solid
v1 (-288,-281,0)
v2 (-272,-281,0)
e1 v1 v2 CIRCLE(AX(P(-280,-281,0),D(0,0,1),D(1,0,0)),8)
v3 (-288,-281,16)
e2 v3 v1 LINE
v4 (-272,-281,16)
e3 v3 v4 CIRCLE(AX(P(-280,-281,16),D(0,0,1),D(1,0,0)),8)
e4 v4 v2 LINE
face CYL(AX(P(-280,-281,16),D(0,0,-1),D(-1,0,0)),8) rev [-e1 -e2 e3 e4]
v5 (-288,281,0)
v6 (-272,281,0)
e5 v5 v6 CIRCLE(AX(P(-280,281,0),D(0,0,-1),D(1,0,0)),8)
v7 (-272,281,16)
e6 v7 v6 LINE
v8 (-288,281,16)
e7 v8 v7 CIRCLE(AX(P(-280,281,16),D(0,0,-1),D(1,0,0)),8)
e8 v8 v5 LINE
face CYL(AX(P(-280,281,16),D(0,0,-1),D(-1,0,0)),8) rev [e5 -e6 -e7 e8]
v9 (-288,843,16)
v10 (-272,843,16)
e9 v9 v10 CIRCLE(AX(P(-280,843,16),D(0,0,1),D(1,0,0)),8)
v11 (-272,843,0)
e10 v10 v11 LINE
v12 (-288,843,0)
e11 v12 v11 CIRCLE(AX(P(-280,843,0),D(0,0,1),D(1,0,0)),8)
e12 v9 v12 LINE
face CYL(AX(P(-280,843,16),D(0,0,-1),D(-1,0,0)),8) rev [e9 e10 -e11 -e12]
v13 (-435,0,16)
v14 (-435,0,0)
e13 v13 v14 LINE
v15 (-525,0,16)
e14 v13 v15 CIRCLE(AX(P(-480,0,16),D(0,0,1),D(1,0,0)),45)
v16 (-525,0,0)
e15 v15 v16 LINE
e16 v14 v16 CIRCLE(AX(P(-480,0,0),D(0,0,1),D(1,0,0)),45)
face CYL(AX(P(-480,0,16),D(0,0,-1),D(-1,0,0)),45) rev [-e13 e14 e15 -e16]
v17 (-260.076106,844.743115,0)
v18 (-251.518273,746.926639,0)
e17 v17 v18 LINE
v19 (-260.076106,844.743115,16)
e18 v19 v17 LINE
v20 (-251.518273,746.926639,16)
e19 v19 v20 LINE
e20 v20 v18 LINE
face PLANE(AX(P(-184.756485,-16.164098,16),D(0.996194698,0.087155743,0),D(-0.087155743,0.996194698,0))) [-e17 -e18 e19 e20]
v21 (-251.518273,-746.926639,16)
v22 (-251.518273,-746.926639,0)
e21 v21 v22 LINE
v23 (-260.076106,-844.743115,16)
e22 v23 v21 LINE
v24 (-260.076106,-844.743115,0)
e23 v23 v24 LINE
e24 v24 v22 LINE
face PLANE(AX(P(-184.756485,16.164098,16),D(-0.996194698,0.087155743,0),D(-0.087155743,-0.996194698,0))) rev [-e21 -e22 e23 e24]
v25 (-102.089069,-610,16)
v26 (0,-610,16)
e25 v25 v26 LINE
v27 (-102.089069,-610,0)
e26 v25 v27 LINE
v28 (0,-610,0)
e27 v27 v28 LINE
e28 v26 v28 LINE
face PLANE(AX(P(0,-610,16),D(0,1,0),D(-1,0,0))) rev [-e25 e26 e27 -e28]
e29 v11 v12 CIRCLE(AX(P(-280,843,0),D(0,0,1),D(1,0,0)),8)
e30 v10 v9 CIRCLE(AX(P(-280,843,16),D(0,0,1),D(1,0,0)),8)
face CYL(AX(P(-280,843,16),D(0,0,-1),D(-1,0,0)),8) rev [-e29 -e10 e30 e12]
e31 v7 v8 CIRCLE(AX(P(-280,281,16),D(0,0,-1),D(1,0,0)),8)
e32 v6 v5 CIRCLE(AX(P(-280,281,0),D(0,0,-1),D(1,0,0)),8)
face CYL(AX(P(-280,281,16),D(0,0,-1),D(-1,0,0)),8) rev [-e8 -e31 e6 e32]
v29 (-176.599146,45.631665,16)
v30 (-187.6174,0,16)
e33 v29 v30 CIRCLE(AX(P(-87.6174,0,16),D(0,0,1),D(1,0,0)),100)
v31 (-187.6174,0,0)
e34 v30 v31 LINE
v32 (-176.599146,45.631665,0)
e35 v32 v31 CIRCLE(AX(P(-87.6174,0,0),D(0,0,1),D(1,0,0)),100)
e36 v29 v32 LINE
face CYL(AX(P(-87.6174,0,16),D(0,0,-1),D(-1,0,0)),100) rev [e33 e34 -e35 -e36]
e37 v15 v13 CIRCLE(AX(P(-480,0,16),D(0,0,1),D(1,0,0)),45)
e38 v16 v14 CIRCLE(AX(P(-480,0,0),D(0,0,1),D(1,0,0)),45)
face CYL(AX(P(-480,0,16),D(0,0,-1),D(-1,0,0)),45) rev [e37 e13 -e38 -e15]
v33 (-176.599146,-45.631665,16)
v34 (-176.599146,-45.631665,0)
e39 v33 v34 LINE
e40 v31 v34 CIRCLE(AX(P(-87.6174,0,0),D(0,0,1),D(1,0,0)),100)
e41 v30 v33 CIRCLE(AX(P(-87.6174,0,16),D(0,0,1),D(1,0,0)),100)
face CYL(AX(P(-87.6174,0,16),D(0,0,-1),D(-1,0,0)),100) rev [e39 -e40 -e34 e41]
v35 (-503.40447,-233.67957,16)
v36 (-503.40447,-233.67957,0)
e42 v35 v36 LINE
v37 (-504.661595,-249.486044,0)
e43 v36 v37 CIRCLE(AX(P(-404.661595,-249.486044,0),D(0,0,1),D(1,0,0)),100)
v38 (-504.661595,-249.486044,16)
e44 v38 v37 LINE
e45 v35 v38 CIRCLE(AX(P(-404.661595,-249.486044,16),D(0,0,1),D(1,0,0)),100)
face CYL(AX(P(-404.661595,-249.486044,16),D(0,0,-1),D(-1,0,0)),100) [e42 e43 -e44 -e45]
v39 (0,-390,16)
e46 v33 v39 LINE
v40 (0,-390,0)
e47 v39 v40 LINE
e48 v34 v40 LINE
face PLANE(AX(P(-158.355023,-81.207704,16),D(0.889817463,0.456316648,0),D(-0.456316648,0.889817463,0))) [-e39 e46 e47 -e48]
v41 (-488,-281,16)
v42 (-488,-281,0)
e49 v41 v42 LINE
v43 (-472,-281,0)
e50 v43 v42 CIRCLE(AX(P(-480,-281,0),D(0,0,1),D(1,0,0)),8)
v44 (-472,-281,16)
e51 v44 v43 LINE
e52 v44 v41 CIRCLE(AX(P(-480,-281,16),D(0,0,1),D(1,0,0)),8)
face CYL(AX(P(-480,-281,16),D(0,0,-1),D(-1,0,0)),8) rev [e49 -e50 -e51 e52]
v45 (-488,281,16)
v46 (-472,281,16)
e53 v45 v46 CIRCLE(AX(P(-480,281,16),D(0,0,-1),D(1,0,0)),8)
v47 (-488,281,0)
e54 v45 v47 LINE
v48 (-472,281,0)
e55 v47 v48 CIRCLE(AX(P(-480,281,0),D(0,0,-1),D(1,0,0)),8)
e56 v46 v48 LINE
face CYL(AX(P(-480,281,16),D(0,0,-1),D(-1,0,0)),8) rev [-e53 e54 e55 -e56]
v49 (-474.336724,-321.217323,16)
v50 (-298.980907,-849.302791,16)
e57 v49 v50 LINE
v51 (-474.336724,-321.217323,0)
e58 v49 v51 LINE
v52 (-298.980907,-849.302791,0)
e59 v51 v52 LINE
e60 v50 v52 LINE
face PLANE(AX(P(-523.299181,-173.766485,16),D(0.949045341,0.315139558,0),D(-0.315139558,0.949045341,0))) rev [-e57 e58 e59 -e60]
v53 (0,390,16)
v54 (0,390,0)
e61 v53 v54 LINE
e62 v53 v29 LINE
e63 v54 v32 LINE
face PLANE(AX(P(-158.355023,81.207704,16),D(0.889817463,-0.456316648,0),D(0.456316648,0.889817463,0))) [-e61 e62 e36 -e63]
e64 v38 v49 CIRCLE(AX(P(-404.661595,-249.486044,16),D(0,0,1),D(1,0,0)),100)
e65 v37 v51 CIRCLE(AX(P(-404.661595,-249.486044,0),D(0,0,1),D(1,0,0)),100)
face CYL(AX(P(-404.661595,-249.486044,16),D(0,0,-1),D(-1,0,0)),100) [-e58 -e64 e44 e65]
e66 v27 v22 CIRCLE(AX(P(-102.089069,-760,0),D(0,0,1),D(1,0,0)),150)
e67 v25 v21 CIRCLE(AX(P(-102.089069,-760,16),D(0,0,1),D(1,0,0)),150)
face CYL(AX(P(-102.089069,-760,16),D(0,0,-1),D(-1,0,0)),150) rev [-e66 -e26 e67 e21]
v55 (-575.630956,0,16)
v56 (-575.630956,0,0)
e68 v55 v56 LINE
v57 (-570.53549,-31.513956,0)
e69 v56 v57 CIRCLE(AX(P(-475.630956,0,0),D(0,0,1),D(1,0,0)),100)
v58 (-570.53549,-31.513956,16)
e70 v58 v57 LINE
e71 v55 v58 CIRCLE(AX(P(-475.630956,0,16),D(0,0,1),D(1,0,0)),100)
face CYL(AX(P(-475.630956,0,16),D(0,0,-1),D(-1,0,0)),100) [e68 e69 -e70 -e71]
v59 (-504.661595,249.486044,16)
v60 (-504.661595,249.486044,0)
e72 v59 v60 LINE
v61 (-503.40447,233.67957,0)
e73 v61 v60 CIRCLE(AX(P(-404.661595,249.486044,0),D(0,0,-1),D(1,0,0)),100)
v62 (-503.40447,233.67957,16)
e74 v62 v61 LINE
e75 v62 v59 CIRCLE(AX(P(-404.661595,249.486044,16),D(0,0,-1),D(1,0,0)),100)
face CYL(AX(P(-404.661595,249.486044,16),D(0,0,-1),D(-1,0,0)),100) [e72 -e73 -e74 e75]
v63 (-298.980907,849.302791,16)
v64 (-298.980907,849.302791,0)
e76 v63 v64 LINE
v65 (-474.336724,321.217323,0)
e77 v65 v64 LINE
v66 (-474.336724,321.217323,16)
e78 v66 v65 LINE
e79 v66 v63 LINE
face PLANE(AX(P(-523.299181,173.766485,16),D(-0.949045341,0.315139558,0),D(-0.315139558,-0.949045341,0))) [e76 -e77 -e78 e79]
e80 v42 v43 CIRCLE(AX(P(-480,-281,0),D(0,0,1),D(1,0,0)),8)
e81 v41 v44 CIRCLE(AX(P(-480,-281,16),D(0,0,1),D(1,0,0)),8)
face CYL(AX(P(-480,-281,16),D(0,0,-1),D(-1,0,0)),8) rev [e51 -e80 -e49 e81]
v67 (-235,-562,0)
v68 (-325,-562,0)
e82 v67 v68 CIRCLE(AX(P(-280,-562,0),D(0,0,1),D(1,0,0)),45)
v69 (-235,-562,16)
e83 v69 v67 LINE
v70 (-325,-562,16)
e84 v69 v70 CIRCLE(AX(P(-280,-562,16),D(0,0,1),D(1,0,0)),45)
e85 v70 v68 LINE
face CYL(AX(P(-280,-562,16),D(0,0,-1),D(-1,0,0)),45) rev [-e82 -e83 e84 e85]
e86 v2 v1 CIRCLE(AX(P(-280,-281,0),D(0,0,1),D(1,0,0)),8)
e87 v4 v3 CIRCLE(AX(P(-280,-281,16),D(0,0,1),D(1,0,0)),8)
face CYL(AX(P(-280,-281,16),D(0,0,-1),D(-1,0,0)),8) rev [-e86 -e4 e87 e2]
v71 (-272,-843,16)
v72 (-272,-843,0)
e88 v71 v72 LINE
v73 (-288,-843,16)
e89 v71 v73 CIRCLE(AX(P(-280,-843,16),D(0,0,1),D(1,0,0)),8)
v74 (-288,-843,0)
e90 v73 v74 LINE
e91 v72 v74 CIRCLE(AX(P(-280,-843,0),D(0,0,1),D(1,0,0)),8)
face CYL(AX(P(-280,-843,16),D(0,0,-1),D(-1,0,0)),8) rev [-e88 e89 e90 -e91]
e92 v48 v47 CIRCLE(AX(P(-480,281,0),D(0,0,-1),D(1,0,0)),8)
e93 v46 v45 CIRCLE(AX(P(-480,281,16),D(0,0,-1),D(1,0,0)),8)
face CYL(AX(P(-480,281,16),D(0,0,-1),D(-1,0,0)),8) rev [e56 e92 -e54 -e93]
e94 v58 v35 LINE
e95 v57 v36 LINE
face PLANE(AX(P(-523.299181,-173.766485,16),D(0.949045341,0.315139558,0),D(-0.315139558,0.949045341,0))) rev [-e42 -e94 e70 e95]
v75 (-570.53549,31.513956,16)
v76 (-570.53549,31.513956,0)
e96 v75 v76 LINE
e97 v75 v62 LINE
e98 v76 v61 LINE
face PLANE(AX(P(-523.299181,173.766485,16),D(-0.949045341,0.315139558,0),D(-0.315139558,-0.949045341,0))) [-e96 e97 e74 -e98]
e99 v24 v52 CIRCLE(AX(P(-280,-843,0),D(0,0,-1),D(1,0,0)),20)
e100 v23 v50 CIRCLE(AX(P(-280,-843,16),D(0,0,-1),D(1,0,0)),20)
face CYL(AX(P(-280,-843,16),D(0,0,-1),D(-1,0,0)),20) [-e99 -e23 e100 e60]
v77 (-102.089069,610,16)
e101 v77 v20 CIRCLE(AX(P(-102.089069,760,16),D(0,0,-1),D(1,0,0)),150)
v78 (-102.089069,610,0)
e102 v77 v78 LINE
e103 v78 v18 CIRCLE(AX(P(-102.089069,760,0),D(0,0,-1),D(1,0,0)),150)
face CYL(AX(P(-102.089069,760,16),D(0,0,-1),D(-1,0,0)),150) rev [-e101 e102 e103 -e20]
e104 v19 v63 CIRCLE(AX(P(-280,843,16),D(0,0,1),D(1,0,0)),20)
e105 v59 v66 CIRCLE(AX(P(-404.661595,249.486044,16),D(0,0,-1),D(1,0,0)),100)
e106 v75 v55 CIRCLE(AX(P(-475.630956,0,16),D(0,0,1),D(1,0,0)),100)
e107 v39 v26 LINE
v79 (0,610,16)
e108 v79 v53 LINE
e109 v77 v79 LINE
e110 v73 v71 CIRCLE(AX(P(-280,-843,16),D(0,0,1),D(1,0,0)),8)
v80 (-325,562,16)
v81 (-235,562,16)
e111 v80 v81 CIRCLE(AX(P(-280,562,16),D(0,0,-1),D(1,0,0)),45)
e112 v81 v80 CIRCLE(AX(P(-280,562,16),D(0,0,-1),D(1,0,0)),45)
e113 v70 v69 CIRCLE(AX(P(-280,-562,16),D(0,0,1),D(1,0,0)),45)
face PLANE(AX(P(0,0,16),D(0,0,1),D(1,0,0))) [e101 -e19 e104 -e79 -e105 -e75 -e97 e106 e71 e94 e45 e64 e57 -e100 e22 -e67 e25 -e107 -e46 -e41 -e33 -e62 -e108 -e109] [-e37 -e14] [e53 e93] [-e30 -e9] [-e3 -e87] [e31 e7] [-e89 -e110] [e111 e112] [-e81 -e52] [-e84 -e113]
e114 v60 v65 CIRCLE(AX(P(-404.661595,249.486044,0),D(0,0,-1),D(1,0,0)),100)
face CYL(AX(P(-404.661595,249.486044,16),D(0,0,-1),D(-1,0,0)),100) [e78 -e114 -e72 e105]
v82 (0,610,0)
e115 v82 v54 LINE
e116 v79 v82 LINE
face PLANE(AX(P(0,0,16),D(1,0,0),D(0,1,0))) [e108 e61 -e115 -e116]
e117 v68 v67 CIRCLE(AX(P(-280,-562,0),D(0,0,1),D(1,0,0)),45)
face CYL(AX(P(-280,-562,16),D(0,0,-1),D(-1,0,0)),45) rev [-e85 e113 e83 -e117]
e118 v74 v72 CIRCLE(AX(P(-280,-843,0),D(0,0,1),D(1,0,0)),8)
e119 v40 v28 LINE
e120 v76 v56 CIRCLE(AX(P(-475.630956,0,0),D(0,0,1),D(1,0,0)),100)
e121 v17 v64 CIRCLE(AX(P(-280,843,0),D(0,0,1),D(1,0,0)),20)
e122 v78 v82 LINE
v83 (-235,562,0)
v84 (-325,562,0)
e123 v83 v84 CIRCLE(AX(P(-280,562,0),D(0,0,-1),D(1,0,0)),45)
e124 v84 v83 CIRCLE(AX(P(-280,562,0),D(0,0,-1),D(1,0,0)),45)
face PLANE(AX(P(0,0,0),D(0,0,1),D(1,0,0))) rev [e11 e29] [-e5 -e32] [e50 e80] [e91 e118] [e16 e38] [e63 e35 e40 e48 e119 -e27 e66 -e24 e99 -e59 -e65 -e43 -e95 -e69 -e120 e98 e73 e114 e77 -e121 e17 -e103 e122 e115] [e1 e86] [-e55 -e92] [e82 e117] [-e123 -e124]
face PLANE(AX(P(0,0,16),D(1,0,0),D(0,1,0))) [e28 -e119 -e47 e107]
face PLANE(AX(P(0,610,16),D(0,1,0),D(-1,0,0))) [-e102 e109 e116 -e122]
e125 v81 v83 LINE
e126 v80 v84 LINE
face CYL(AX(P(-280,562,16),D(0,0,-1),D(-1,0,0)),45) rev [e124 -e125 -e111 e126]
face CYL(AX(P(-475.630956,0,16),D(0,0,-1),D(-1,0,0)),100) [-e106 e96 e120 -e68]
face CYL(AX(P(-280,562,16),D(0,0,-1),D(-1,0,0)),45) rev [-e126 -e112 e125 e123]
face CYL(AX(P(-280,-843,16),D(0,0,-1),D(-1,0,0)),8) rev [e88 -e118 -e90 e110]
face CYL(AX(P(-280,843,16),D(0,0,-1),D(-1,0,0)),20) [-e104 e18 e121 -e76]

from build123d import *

# Parameters (mm, degrees)
SKETCH1_R           = 45
SKETCH1_R_2         = 3.5
SKETCH1_R_3         = 8
BOSS_EXTRUDE1_DEPTH = 16
BOSS_EXTRUDE2_START = -16
SKETCH4_R           = 3.5
BOSS_EXTRUDE2_DEPTH = 16


with BuildPart() as part:
    # Sketch1 → Boss-Extrude1 (new body)
    with BuildSketch(Plane.XY):
        with BuildLine():
            Line((-570.535490362, 31.513955821), (-503.404469767, 233.679569935))
            ThreePointArc((-503.404469767, 233.679569935), (-499.566128801, 281), (-474.336723785, 321.217323201))
            Line((-474.336723785, 321.217323201), (-298.980906816, 849.302791164))
            ThreePointArc((-298.980906816, 849.302791164), (-277.671917484, 862.864038658), (-260.076106038, 844.743114855))
            Line((-260.076106038, 844.743114855), (-251.518273259, 746.926638588))
            ThreePointArc((-251.518273259, 746.926638588), (-203.427599687, 649.408399478), (-102.089068545, 610))
            Line((-102.089068545, 610), (0, 610))
            Line((0, 610), (0, 390))
            Line((0, 390), (-176.599146277, 45.63166476))
            ThreePointArc((-176.599146277, 45.63166476), (-187.617399996, 0), (-176.599146277, -45.63166476))
            Line((-176.599146277, -45.63166476), (0, -390))
            Line((0, -390), (0, -610))
            Line((0, -610), (-102.089068545, -610))
            ThreePointArc((-102.089068545, -610), (-203.427599687, -649.408399478), (-251.518273259, -746.926638588))
            Line((-251.518273259, -746.926638588), (-260.076106038, -844.743114855))
            ThreePointArc((-260.076106038, -844.743114855), (-277.671917484, -862.864038658), (-298.980906816, -849.302791164))
            Line((-298.980906816, -849.302791164), (-474.336723785, -321.217323201))
            ThreePointArc((-474.336723785, -321.217323201), (-499.566128801, -281), (-503.404469767, -233.679569935))
            Line((-503.404469767, -233.679569935), (-570.535490362, -31.513955821))
            ThreePointArc((-570.535490362, -31.513955821), (-575.630956285, 0), (-570.535490362, 31.513955821))
        make_face()
        with Locations((-280, 562)):
            Circle(SKETCH1_R, mode=Mode.SUBTRACT)
        with Locations((-355, 582)):
            Circle(SKETCH1_R_2, mode=Mode.SUBTRACT)
        with Locations((-280, 281)):
            Circle(SKETCH1_R_3, mode=Mode.SUBTRACT)
        with Locations((-355, -582)):
            Circle(SKETCH1_R_2, mode=Mode.SUBTRACT)
        with Locations((-355, -542)):
            Circle(SKETCH1_R_2, mode=Mode.SUBTRACT)
        with Locations((-405, -20)):
            Circle(SKETCH1_R_2, mode=Mode.SUBTRACT)
        with Locations((-405, 20)):
            Circle(SKETCH1_R_2, mode=Mode.SUBTRACT)
        with Locations((-280, 843)):
            Circle(SKETCH1_R_3, mode=Mode.SUBTRACT)
        with Locations((-280, -843)):
            Circle(SKETCH1_R_3, mode=Mode.SUBTRACT)
        with Locations((-280, -281)):
            Circle(SKETCH1_R_3, mode=Mode.SUBTRACT)
        with Locations((-480, -281)):
            Circle(SKETCH1_R_3, mode=Mode.SUBTRACT)
        with Locations((-280, -562)):
            Circle(SKETCH1_R, mode=Mode.SUBTRACT)
        with Locations((-480, 0)):
            Circle(SKETCH1_R, mode=Mode.SUBTRACT)
        with Locations((-480, 281)):
            Circle(SKETCH1_R_3, mode=Mode.SUBTRACT)
        with Locations((-355, 542)):
            Circle(SKETCH1_R_2, mode=Mode.SUBTRACT)
    extrude(amount=BOSS_EXTRUDE1_DEPTH)

    # Sketch4 → Boss-Extrude2 (add)
    with BuildSketch(Plane.XY.offset(16).offset(BOSS_EXTRUDE2_START)):
        with Locations((-355, -542)):
            Circle(SKETCH4_R)
        with Locations((-355, -582)):
            Circle(SKETCH4_R)
        with Locations((-405, -20)):
            Circle(SKETCH4_R)
        with Locations((-405, 20)):
            Circle(SKETCH4_R)
        with Locations((-355, 542)):
            Circle(SKETCH4_R)
        with Locations((-355, 582)):
            Circle(SKETCH4_R)
    extrude(amount=BOSS_EXTRUDE2_DEPTH)


solid = part.part
